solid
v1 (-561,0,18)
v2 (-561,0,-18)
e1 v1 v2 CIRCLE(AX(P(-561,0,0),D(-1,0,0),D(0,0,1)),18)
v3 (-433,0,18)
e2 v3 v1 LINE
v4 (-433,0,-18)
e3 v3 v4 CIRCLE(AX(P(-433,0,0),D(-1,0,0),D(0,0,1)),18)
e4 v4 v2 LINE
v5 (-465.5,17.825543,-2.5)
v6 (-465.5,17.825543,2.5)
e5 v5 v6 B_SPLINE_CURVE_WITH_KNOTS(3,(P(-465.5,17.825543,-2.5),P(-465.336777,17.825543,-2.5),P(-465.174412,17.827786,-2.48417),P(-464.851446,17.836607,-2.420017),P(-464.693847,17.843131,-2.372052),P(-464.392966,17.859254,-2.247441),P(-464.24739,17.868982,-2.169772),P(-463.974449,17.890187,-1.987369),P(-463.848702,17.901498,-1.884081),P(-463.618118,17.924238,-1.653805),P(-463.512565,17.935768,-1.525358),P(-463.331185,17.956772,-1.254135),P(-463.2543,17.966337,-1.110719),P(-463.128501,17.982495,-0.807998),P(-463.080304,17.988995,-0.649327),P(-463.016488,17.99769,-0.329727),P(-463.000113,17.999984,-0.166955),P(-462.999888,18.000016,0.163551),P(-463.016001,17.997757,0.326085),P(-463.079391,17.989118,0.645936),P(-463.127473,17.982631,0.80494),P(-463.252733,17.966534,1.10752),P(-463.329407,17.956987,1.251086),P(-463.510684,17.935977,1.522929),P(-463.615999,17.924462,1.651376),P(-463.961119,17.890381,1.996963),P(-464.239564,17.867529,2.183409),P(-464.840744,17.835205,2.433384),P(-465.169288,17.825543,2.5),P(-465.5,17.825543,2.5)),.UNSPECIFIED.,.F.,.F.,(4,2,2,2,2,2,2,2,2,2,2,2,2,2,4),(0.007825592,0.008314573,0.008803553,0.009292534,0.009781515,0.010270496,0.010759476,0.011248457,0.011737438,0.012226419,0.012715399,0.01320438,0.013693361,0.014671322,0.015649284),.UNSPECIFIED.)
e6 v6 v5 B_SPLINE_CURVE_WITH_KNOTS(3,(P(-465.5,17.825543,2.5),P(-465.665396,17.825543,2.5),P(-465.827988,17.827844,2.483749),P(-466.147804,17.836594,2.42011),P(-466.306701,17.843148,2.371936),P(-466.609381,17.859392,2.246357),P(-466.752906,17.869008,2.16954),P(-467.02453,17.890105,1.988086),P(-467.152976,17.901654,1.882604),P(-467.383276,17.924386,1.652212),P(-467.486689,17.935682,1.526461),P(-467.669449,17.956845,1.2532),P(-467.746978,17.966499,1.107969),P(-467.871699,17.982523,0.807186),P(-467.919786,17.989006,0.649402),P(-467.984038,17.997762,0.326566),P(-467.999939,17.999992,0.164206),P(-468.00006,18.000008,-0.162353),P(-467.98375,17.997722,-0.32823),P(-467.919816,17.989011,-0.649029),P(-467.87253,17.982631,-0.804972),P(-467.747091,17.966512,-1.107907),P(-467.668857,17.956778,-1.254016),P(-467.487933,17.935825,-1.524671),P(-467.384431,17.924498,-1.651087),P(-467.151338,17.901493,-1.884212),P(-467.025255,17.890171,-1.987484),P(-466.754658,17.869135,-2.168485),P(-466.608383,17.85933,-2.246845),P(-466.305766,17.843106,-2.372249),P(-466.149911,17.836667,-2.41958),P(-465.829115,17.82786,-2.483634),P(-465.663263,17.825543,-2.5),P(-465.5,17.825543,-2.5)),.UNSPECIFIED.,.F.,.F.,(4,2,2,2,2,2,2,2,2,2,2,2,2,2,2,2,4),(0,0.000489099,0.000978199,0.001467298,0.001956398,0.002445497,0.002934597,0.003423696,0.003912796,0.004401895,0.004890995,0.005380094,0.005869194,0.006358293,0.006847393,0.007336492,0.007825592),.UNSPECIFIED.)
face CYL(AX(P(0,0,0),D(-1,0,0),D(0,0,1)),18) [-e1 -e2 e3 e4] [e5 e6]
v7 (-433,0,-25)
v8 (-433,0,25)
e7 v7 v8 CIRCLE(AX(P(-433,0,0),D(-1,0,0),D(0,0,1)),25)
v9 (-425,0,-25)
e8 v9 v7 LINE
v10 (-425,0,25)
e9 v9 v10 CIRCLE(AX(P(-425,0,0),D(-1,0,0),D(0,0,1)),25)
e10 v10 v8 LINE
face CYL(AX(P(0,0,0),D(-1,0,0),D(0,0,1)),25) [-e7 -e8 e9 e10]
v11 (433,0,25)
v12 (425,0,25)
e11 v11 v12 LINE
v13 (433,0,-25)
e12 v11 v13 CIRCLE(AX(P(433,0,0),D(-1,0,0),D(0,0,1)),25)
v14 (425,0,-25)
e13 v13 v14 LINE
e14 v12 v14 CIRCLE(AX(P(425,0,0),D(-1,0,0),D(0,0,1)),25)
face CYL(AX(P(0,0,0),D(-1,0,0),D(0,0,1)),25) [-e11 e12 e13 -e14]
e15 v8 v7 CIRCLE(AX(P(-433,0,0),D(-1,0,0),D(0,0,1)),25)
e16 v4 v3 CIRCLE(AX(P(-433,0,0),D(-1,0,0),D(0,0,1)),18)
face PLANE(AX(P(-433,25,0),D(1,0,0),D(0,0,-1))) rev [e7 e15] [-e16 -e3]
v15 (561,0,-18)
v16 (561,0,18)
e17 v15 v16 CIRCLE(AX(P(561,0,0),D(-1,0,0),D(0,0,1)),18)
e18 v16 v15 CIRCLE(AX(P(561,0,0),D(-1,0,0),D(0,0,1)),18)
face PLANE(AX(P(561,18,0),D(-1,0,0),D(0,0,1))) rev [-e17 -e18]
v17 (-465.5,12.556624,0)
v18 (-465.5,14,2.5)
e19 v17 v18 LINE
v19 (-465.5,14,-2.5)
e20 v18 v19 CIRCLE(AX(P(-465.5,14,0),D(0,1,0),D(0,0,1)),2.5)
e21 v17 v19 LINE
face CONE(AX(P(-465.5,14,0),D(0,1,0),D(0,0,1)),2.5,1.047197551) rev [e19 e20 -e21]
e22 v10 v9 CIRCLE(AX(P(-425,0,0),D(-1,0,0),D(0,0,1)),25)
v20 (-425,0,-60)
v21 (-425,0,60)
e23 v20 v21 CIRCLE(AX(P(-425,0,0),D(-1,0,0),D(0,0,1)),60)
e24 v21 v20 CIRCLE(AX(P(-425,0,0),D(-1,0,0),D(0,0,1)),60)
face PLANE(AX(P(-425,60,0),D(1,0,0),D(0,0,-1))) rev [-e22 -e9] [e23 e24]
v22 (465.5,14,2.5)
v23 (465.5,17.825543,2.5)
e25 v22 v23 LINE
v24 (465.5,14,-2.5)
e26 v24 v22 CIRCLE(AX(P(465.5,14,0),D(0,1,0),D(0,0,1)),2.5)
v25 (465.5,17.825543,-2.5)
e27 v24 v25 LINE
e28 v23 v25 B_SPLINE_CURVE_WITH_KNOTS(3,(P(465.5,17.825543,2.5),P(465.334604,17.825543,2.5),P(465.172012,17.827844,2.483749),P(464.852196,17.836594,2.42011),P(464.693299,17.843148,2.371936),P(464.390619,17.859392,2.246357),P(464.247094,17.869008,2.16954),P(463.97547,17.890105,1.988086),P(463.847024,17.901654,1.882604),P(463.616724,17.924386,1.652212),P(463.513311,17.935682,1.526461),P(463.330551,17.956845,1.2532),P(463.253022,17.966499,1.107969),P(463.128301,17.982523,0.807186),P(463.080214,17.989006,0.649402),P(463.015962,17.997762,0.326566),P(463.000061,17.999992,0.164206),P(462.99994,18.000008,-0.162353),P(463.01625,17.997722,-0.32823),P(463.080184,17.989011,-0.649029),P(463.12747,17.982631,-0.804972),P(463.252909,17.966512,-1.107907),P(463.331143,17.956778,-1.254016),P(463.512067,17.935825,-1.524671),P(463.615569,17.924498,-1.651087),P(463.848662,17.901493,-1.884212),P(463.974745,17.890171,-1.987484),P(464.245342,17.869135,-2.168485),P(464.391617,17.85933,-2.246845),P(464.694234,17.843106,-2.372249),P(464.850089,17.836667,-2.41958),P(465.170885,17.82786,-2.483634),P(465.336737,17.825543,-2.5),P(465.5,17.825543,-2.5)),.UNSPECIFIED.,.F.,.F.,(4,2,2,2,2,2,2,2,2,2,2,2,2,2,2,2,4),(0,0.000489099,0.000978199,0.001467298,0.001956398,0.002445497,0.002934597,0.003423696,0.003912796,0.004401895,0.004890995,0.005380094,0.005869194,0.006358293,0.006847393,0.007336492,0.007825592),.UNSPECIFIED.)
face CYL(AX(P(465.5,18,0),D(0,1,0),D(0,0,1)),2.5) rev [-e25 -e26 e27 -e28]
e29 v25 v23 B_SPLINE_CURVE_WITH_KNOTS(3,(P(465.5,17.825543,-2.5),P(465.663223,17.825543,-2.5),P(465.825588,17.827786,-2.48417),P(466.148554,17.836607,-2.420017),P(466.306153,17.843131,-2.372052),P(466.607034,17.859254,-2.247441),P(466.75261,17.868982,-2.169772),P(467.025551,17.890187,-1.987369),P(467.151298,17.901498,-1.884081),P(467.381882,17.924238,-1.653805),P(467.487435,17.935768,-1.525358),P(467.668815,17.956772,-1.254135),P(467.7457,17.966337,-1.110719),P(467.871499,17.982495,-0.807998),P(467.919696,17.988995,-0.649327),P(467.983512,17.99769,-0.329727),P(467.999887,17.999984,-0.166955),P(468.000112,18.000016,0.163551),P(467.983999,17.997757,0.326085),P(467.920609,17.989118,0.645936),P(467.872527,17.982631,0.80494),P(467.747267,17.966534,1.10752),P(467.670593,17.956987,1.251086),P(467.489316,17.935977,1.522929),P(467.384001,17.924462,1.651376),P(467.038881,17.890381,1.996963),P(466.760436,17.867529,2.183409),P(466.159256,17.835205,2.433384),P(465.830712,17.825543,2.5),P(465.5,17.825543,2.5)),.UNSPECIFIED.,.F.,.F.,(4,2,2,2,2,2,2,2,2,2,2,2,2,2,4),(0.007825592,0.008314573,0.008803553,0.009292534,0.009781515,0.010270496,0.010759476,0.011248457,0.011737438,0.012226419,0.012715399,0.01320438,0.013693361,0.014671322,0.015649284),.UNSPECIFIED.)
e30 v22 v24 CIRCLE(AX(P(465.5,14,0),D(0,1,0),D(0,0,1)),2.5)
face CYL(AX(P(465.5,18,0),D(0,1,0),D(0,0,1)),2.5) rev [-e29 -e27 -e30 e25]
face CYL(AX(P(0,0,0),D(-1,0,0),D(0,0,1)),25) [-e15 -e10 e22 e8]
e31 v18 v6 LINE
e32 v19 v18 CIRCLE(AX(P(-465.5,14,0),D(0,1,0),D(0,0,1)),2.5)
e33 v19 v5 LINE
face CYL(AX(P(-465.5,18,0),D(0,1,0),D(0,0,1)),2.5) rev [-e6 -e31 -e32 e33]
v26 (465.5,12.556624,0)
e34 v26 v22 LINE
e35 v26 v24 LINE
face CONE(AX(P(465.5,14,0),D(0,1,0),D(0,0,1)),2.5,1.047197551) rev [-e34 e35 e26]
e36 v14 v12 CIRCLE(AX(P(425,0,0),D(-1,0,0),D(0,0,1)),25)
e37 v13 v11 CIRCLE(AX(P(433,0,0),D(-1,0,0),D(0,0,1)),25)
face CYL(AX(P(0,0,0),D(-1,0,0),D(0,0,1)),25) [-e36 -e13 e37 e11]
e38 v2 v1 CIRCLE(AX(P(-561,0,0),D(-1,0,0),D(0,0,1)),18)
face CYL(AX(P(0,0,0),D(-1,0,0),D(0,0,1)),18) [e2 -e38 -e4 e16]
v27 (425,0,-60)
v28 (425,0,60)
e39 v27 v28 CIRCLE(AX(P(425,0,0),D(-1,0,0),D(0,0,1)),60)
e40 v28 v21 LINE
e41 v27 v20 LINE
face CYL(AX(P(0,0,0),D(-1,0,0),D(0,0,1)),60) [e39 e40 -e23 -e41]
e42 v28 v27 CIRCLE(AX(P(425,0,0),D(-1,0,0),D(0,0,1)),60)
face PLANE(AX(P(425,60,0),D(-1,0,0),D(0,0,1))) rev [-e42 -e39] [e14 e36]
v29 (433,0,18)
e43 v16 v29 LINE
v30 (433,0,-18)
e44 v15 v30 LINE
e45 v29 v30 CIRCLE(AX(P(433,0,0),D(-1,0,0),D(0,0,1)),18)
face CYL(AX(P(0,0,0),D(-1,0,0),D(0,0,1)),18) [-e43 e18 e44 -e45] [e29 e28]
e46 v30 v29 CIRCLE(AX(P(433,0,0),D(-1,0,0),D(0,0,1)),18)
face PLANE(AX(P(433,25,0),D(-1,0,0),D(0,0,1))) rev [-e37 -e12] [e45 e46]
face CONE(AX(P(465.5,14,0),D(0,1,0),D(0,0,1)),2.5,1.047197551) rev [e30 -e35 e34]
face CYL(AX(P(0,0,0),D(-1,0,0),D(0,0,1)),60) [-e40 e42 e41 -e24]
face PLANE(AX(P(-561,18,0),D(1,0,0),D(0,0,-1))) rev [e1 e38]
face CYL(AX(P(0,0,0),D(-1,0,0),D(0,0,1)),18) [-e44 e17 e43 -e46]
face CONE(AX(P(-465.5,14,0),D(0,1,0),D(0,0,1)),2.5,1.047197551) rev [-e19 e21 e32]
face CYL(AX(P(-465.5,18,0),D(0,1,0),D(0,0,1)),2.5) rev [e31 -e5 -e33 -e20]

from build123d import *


with BuildPart() as part:
    # 草图1 → 旋转1 (revolve)
    with BuildSketch(Plane.XY, mode=Mode.PRIVATE) as revolve_1_sk:
        Polygon((-425, 60), (425, 60), (425, 25), (433, 25), (433, 18), (561, 18), (561, 0), (-561, 0), (-561, 18), (-433, 18), (-433, 25), (-425, 25), align=None)
    revolve(revolve_1_sk.sketch.rotate(Axis((0, 0, 0), (1, 0, 0)), 90), axis=Axis((0, 0, 0), (1, 0, 0)))

    # 草图2 → M6 螺纹孔1 (revolve, cut)
    with BuildSketch(Plane(origin=(465.5, 18, 0), x_dir=(0, 0, 1), z_dir=(1, 0, 0))):
        Polygon((0, 0), (0, 5.443375673), (2.5, 4), (2.5, 0), align=None)
    hole_wizard_m6_1 = revolve(axis=Axis((465.5, 24.35, 0), (0, -1, 0)), mode=Mode.SUBTRACT)

    # 镜向1: M6 螺纹孔1 across plane
    add(hole_wizard_m6_1.mirror(Plane(origin=(0, 0, 0), x_dir=(0, 0, 1), z_dir=(1, 0, 0))), mode=Mode.SUBTRACT)


solid = part.part
